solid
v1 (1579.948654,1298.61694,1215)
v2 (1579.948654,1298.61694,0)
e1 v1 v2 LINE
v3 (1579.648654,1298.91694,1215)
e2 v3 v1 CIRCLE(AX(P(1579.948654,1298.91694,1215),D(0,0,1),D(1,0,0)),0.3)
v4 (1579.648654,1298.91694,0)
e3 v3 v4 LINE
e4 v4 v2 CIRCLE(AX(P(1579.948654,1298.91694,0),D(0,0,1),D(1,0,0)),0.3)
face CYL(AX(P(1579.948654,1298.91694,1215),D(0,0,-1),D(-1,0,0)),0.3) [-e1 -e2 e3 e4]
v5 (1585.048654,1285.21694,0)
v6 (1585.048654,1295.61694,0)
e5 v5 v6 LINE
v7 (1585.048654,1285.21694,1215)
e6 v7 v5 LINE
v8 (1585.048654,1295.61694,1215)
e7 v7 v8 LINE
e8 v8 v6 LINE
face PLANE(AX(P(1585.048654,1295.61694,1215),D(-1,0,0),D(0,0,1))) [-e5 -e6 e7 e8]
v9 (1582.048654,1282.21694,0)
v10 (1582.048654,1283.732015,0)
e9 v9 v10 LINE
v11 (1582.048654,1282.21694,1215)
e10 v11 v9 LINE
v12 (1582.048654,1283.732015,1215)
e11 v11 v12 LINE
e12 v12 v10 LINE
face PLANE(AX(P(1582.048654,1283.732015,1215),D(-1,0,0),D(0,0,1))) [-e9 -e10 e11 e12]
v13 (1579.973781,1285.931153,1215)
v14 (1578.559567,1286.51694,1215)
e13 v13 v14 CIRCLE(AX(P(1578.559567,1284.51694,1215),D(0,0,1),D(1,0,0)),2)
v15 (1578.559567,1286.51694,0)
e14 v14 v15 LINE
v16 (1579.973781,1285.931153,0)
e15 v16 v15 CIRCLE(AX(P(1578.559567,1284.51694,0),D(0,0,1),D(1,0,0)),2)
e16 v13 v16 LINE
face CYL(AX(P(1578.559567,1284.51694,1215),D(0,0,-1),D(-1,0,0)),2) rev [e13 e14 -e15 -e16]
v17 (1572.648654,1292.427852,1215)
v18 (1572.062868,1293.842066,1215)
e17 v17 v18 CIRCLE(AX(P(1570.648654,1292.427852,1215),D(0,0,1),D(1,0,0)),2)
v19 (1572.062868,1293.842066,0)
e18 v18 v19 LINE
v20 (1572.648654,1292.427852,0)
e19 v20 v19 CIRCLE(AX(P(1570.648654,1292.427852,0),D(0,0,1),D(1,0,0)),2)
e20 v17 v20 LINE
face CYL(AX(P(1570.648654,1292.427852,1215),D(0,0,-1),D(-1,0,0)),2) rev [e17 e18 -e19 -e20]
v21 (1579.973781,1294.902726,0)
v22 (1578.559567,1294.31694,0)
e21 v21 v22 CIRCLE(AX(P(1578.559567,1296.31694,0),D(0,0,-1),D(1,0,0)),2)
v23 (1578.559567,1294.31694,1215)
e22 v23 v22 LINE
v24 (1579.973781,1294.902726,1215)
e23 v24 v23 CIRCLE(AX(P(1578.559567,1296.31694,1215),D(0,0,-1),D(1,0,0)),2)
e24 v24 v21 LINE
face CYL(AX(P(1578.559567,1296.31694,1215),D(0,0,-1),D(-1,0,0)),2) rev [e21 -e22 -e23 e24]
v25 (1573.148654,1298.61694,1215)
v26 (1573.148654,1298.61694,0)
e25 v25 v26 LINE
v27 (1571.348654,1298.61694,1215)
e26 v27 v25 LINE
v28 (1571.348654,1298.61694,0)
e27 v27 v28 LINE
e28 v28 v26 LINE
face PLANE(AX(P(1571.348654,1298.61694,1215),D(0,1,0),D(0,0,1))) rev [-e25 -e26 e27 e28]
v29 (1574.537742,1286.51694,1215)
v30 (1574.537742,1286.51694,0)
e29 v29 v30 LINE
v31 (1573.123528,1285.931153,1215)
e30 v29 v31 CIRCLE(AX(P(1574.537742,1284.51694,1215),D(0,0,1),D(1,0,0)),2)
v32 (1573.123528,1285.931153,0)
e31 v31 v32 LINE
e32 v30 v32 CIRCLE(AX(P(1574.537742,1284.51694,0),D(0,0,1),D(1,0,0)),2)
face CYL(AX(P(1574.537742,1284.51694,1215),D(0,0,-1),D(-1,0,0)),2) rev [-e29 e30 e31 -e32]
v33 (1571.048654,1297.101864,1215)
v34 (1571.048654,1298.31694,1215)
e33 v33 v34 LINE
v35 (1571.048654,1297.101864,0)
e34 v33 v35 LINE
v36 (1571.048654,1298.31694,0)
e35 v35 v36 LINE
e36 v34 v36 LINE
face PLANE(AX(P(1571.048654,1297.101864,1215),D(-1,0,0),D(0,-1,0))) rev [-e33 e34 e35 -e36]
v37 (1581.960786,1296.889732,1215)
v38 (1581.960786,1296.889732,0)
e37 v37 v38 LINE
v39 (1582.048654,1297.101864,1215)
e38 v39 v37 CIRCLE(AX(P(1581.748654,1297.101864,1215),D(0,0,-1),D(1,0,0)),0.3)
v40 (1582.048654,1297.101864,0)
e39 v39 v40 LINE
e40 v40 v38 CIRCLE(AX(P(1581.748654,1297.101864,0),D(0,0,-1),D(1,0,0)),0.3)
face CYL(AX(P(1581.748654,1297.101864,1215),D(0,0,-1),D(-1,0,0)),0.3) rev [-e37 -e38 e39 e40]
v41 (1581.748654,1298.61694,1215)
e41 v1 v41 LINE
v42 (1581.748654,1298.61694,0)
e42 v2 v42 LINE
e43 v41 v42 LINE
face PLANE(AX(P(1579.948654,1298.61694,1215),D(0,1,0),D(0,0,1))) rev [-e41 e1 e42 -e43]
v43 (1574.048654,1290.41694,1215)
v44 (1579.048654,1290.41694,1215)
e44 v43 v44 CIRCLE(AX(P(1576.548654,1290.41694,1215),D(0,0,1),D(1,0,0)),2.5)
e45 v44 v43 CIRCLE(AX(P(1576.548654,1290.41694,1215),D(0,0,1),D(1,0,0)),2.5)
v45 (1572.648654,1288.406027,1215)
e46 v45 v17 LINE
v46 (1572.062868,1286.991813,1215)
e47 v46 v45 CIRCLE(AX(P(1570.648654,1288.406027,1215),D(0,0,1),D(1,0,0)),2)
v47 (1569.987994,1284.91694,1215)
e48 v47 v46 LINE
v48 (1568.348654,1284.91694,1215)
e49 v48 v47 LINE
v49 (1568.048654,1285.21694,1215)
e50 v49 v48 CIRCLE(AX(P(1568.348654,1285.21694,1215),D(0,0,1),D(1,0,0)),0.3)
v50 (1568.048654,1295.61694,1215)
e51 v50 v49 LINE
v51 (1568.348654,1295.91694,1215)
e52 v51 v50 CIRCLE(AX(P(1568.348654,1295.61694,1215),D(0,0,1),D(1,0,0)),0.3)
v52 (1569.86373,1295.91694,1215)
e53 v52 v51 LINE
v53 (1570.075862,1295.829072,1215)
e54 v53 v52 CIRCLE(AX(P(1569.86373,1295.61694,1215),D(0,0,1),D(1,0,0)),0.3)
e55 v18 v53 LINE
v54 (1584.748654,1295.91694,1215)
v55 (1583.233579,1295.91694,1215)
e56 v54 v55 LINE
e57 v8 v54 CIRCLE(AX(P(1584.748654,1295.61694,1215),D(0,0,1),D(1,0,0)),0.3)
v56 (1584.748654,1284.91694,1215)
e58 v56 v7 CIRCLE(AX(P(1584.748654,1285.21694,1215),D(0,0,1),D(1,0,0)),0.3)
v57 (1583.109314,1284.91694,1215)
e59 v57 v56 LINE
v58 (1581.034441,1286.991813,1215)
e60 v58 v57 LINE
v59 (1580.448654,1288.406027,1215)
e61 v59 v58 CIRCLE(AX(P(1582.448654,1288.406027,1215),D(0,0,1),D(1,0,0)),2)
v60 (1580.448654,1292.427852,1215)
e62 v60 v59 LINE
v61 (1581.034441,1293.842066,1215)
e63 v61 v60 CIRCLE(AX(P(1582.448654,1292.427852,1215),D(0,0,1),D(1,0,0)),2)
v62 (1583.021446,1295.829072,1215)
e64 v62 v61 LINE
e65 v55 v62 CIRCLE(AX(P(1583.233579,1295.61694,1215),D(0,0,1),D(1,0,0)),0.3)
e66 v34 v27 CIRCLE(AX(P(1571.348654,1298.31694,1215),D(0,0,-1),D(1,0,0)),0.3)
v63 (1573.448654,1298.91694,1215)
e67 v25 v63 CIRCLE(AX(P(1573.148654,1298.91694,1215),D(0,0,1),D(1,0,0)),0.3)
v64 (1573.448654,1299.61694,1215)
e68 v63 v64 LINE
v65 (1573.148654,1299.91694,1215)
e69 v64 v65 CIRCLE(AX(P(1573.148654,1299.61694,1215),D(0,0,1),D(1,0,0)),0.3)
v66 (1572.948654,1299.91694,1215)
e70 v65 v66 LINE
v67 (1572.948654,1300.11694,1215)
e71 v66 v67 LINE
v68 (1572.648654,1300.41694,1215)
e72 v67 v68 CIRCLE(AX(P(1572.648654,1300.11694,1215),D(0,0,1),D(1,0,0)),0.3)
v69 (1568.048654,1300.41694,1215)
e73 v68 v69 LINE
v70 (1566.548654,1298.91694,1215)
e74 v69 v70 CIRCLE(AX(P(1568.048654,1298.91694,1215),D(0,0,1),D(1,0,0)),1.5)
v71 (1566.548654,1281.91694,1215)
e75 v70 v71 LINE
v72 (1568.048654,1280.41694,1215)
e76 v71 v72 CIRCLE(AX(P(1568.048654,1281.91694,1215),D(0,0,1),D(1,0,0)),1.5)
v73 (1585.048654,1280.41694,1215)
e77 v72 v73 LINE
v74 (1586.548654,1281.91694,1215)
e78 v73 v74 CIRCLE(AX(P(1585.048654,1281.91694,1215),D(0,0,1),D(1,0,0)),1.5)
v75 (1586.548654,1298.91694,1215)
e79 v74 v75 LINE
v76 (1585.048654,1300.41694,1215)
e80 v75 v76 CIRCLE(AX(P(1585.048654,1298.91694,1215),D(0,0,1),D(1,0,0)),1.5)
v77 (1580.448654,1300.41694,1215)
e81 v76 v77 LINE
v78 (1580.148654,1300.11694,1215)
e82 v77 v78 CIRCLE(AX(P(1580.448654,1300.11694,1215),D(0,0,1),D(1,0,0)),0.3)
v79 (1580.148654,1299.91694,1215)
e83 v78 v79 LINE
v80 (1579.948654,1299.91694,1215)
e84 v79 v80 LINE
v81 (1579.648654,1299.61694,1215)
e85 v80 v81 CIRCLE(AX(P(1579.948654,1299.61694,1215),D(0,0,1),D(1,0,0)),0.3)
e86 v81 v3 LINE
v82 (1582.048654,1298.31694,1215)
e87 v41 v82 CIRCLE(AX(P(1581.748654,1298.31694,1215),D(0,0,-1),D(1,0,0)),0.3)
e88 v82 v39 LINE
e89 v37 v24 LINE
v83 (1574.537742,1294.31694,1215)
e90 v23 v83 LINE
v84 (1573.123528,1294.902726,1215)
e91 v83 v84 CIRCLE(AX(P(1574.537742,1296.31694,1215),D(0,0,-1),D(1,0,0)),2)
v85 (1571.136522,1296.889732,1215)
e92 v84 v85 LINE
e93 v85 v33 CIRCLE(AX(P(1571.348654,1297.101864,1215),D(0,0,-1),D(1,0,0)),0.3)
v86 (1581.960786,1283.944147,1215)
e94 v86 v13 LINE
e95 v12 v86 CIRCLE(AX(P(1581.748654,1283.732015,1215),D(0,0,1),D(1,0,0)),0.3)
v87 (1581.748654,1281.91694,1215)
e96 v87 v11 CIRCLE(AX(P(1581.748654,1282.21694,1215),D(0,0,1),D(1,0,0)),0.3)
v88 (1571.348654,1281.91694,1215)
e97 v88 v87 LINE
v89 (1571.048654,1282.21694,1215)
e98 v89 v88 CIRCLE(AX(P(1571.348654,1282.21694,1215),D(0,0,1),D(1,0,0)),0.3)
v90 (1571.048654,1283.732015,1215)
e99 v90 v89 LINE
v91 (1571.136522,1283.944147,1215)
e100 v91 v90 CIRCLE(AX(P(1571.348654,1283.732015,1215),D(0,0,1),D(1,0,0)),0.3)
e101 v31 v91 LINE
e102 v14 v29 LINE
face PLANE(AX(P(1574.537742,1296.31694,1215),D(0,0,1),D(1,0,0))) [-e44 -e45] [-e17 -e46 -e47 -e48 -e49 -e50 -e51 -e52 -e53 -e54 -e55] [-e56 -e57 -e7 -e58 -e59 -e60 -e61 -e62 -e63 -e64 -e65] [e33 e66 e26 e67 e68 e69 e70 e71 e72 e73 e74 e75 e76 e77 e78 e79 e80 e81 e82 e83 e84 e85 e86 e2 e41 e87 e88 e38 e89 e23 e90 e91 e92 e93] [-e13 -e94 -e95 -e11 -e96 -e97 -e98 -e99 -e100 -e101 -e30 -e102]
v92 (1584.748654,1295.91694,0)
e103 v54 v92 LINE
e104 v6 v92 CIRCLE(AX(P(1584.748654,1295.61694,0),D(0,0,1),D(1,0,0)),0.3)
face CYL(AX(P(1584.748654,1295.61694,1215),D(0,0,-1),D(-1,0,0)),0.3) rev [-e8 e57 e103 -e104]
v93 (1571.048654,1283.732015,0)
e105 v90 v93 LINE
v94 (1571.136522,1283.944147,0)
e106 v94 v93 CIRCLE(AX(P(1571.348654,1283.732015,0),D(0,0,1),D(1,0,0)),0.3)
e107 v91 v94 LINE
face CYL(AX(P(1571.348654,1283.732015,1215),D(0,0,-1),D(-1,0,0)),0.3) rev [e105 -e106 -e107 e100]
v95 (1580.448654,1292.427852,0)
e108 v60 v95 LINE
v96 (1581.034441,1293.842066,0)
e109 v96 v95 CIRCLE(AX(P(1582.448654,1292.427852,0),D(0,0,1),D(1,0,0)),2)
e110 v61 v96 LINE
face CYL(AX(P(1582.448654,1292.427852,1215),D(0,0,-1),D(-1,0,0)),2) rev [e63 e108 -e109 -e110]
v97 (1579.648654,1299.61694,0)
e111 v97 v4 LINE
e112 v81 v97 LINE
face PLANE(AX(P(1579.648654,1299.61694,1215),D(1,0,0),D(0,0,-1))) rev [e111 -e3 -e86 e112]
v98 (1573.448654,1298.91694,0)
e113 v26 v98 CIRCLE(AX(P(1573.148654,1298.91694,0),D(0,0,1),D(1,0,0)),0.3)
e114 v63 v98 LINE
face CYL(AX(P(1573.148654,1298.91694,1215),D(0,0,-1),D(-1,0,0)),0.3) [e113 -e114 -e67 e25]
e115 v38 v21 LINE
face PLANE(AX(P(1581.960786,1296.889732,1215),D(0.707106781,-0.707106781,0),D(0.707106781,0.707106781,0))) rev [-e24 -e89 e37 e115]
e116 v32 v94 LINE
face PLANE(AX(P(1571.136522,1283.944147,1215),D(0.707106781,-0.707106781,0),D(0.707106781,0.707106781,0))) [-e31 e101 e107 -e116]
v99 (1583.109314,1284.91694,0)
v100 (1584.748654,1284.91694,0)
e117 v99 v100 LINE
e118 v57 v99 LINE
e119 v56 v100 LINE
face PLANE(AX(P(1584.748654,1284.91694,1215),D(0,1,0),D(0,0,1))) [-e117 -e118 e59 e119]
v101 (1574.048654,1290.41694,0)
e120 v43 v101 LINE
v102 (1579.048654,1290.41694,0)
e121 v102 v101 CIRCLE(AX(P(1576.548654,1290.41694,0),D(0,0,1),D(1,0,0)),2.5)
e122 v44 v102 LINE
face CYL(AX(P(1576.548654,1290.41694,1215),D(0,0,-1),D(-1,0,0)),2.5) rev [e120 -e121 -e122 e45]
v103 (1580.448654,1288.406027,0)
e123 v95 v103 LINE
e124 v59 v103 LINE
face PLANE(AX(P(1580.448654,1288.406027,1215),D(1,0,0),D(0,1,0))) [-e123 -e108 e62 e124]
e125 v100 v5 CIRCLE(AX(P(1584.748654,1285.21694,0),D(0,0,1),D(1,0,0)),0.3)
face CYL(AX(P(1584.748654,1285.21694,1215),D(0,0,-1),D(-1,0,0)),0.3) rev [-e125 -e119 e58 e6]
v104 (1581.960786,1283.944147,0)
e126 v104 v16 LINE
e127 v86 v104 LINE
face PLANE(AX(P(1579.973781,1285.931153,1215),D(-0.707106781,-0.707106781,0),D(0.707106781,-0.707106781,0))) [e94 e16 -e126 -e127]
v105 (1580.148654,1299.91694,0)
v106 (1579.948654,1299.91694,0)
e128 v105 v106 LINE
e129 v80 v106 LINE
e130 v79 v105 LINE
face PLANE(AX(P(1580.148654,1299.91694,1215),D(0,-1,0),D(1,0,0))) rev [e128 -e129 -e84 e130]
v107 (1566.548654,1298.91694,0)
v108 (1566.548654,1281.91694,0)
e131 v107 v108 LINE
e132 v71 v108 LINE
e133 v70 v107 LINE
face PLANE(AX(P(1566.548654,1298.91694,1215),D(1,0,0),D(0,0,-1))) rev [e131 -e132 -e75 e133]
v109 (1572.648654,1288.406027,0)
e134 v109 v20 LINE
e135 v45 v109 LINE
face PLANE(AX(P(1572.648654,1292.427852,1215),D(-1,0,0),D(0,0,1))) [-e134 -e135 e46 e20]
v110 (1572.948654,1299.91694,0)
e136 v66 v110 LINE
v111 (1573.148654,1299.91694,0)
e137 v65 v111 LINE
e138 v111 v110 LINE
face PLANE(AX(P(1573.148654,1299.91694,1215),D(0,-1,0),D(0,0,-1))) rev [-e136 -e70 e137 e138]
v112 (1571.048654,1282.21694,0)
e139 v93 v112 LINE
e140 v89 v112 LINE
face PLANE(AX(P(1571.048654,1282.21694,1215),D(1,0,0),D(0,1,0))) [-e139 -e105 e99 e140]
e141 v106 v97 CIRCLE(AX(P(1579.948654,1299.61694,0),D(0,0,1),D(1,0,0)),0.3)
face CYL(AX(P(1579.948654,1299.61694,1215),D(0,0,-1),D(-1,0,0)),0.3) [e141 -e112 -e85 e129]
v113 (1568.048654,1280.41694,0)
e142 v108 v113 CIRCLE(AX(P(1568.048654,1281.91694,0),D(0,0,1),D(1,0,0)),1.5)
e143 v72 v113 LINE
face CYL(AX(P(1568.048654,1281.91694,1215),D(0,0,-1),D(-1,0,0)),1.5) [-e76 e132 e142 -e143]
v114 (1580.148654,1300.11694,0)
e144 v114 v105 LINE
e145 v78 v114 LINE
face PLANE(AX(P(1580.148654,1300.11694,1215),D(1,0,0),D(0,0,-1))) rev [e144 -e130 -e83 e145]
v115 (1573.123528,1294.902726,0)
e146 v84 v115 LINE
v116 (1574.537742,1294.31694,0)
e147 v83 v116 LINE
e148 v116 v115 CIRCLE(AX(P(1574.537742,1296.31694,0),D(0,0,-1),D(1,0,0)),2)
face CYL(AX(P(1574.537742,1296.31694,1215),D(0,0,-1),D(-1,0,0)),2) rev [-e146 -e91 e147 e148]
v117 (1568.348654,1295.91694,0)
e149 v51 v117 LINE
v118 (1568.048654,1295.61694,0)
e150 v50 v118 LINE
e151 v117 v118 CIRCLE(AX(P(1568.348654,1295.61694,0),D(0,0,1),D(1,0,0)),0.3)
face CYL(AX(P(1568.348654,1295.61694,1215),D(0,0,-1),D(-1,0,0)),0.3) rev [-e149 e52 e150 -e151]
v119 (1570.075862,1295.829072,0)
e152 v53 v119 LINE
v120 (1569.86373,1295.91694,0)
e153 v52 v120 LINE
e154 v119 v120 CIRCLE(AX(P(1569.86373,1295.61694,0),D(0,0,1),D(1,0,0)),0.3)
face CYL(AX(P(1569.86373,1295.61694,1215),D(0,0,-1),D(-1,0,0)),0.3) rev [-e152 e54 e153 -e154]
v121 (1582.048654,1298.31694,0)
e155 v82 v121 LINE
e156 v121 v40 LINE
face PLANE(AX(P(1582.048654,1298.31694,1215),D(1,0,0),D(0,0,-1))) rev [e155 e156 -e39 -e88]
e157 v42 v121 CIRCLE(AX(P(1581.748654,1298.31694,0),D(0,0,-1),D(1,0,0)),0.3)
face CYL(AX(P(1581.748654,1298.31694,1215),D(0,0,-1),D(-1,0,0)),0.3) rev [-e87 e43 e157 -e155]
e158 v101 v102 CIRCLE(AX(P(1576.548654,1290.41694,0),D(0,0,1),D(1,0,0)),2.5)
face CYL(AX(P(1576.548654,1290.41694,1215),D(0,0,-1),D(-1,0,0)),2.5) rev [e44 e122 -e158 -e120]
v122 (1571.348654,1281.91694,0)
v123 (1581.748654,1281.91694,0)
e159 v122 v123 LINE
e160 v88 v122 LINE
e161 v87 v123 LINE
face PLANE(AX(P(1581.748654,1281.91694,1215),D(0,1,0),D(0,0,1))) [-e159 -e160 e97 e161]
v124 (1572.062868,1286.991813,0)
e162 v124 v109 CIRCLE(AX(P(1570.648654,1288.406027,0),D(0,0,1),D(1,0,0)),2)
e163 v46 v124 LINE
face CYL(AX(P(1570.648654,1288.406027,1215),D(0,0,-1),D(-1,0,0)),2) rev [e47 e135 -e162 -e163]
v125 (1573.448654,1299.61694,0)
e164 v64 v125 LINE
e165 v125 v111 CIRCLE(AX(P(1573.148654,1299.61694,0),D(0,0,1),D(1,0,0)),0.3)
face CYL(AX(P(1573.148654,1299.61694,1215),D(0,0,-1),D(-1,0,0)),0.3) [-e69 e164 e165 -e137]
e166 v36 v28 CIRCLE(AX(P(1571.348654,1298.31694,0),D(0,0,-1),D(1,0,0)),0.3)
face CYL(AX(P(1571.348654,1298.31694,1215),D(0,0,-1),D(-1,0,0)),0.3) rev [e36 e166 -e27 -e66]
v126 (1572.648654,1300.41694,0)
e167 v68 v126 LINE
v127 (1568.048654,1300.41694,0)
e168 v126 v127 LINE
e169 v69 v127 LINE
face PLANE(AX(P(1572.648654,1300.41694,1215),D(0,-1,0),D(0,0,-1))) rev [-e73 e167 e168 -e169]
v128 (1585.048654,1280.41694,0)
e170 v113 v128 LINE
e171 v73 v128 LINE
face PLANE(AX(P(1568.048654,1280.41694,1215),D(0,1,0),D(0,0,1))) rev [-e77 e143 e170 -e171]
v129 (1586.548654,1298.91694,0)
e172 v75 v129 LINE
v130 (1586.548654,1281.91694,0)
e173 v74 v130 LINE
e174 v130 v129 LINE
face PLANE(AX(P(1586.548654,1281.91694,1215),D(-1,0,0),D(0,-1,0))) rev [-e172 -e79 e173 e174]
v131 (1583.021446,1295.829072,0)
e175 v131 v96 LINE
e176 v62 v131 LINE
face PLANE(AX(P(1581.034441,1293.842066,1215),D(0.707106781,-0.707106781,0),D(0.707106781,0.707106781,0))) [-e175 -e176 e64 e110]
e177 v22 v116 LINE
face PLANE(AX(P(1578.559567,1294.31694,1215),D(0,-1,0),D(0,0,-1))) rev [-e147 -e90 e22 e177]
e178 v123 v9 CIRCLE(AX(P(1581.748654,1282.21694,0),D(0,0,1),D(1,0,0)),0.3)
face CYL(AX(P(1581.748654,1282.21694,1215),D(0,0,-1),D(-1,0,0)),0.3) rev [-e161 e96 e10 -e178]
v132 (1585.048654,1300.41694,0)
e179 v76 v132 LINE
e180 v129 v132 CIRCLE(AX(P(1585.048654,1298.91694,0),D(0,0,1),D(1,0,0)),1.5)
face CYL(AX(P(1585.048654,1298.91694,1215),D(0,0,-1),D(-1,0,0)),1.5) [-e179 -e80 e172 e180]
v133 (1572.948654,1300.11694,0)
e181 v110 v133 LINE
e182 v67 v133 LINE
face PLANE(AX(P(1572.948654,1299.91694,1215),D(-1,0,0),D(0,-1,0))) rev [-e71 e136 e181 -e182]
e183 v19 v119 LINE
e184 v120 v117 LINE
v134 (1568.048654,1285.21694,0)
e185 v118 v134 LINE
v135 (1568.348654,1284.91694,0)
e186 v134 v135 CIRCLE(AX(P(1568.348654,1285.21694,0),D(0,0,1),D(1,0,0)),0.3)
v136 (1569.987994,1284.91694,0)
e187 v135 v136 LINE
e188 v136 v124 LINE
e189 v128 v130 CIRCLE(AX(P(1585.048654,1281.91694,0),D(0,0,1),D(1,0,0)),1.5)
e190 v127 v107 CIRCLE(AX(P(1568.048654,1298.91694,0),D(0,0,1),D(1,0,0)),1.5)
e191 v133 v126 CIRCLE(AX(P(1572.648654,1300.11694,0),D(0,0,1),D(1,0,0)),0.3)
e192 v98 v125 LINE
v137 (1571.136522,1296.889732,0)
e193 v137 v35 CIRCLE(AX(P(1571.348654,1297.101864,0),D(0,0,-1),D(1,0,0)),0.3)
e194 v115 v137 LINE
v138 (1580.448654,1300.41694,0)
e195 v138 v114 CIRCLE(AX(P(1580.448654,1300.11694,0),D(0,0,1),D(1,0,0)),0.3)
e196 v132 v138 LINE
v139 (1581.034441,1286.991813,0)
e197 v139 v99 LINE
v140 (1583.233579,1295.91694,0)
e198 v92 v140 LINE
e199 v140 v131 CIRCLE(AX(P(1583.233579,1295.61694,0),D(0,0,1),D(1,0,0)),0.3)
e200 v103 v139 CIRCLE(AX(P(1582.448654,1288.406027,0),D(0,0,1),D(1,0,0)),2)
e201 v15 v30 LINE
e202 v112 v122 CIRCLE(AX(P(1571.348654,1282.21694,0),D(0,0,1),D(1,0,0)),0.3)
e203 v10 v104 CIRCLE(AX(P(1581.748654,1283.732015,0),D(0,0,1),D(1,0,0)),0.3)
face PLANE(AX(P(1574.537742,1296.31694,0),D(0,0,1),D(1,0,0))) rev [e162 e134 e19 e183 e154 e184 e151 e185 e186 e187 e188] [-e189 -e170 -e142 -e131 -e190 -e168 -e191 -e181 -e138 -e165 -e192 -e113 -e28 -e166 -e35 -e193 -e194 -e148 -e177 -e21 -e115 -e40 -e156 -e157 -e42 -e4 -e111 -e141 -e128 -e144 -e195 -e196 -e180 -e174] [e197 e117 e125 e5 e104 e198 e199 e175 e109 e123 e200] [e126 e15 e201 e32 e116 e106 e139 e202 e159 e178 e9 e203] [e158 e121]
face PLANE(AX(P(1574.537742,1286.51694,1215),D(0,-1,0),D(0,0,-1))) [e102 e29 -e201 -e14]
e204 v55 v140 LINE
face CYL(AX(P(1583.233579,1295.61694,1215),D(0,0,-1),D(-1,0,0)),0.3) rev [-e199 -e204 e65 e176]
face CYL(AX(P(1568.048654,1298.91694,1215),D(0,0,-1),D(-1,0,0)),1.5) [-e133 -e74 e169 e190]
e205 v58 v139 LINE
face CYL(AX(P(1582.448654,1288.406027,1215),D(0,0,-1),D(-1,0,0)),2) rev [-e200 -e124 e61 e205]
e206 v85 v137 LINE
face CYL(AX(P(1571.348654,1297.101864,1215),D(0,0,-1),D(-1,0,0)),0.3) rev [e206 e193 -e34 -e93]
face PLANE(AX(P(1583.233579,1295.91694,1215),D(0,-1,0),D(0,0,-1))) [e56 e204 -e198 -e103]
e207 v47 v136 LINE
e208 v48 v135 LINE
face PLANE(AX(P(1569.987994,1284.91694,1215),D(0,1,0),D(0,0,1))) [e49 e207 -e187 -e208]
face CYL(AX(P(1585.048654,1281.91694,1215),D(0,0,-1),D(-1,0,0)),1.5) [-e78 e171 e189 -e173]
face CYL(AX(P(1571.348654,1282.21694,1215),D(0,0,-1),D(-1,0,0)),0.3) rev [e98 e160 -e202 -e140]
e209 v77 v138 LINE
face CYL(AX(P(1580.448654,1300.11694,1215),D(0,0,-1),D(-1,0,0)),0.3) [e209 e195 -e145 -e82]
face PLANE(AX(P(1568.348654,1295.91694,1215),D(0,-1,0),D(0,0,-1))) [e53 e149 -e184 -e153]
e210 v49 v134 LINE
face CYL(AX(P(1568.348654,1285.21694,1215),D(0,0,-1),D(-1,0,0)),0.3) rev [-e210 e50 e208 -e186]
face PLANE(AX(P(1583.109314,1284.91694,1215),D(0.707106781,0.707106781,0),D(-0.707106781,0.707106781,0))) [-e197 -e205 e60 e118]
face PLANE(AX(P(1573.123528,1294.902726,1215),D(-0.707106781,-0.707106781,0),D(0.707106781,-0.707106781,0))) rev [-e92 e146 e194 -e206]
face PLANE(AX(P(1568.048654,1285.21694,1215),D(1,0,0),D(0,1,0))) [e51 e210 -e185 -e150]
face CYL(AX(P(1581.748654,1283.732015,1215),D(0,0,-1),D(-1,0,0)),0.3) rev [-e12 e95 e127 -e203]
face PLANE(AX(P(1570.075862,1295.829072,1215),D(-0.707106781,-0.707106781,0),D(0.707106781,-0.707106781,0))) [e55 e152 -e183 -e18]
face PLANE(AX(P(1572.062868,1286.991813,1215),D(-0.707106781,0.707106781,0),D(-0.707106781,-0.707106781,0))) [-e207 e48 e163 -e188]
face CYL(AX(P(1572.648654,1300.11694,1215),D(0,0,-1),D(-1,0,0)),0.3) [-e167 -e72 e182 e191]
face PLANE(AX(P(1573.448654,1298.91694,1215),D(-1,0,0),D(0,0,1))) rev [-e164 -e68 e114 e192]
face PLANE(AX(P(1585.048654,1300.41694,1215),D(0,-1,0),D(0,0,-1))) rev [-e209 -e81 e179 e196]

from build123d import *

# Parameters (mm, degrees)
SKETCH_1_R      = 2.5
EXTRUDE_1_DEPTH = 1215


with BuildPart() as part:
    # 草图1 → 凸台-拉伸1 (new body)
    with BuildSketch(Plane.XY):
        with BuildLine():
            Line((1573.123527995, 1294.902726123), (1571.136522226, 1296.889731891))
            ThreePointArc((1571.136522226, 1296.889731891), (1571.071490401, 1296.987058896), (1571.048654261, 1297.101863926))
            Line((1571.048654261, 1297.101863926), (1571.048654261, 1298.316939685))
            ThreePointArc((1571.048654261, 1298.316939685), (1571.136522226, 1298.52907172), (1571.348654261, 1298.616939685))
            Line((1571.348654261, 1298.616939685), (1573.148654261, 1298.616939685))
            ThreePointArc((1573.148654261, 1298.616939685), (1573.360786295, 1298.704807651), (1573.448654261, 1298.916939685))
            Line((1573.448654261, 1298.916939685), (1573.448654261, 1299.616939685))
            ThreePointArc((1573.448654261, 1299.616939685), (1573.360786295, 1299.82907172), (1573.148654261, 1299.916939685))
            Line((1573.148654261, 1299.916939685), (1572.948654261, 1299.916939685))
            Line((1572.948654261, 1299.916939685), (1572.948654261, 1300.116939685))
            ThreePointArc((1572.948654261, 1300.116939685), (1572.860786295, 1300.32907172), (1572.648654261, 1300.416939685))
            Line((1572.648654261, 1300.416939685), (1568.048654261, 1300.416939685))
            ThreePointArc((1568.048654261, 1300.416939685), (1566.987994089, 1299.977599857), (1566.548654261, 1298.916939685))
            Line((1566.548654261, 1298.916939685), (1566.548654261, 1281.916939685))
            ThreePointArc((1566.548654261, 1281.916939685), (1566.987994089, 1280.856279514), (1568.048654261, 1280.416939685))
            Line((1568.048654261, 1280.416939685), (1585.048654261, 1280.416939685))
            ThreePointArc((1585.048654261, 1280.416939685), (1586.109314432, 1280.856279514), (1586.548654261, 1281.916939685))
            Line((1586.548654261, 1281.916939685), (1586.548654261, 1298.916939685))
            ThreePointArc((1586.548654261, 1298.916939685), (1586.109314432, 1299.977599857), (1585.048654261, 1300.416939685))
            Line((1585.048654261, 1300.416939685), (1580.448654261, 1300.416939685))
            ThreePointArc((1580.448654261, 1300.416939685), (1580.236522226, 1300.32907172), (1580.148654261, 1300.116939685))
            Line((1580.148654261, 1300.116939685), (1580.148654261, 1299.916939685))
            Line((1580.148654261, 1299.916939685), (1579.948654261, 1299.916939685))
            ThreePointArc((1579.948654261, 1299.916939685), (1579.736522226, 1299.82907172), (1579.648654261, 1299.616939685))
            Line((1579.648654261, 1299.616939685), (1579.648654261, 1298.916939685))
            ThreePointArc((1579.648654261, 1298.916939685), (1579.736522226, 1298.704807651), (1579.94865426, 1298.616939685))
            Line((1579.94865426, 1298.616939685), (1581.748654261, 1298.616939685))
            ThreePointArc((1581.748654261, 1298.616939685), (1581.960786295, 1298.52907172), (1582.048654261, 1298.316939685))
            Line((1582.048654261, 1298.316939685), (1582.048654261, 1297.101863926))
            ThreePointArc((1582.048654261, 1297.101863926), (1582.02581812, 1296.987058896), (1581.960786295, 1296.889731891))
            Line((1581.960786295, 1296.889731891), (1579.973780526, 1294.902726123))
            ThreePointArc((1579.973780526, 1294.902726123), (1579.324933829, 1294.46918062), (1578.559566964, 1294.316939685))
            Line((1578.559566964, 1294.316939685), (1574.537741557, 1294.316939685))
            ThreePointArc((1574.537741557, 1294.316939685), (1573.772374693, 1294.46918062), (1573.123527995, 1294.902726123))
        make_face()
        with Locations((1576.548654261, 1290.416939685)):
            Circle(SKETCH_1_R, mode=Mode.SUBTRACT)
        with BuildLine():
            Line((1572.648654261, 1292.427852389), (1572.648654261, 1288.406026982))
            ThreePointArc((1572.648654261, 1288.406026982), (1572.496413326, 1287.640660117), (1572.062867823, 1286.99181342))
            Line((1572.062867823, 1286.99181342), (1569.987994089, 1284.916939685))
            Line((1569.987994089, 1284.916939685), (1568.348654261, 1284.916939685))
            ThreePointArc((1568.348654261, 1284.916939685), (1568.136522226, 1285.004807651), (1568.048654261, 1285.216939685))
            Line((1568.048654261, 1285.216939685), (1568.048654261, 1295.616939685))
            ThreePointArc((1568.048654261, 1295.616939685), (1568.136522226, 1295.82907172), (1568.348654261, 1295.916939685))
            Line((1568.348654261, 1295.916939685), (1569.86373002, 1295.916939685))
            ThreePointArc((1569.86373002, 1295.916939685), (1569.97853505, 1295.894103545), (1570.075862055, 1295.82907172))
            Line((1570.075862055, 1295.82907172), (1572.062867823, 1293.842065951))
            ThreePointArc((1572.062867823, 1293.842065951), (1572.496413326, 1293.193219254), (1572.648654261, 1292.427852389))
        make_face(mode=Mode.SUBTRACT)
        with BuildLine():
            Line((1581.034440698, 1293.842065951), (1583.021446467, 1295.82907172))
            ThreePointArc((1583.021446467, 1295.82907172), (1583.118773471, 1295.894103545), (1583.233578501, 1295.916939685))
            Line((1583.233578501, 1295.916939685), (1584.748654261, 1295.916939685))
            ThreePointArc((1584.748654261, 1295.916939685), (1584.960786295, 1295.82907172), (1585.048654261, 1295.616939685))
            Line((1585.048654261, 1295.616939685), (1585.048654261, 1285.216939685))
            ThreePointArc((1585.048654261, 1285.216939685), (1584.960786295, 1285.004807651), (1584.748654261, 1284.916939685))
            Line((1584.748654261, 1284.916939685), (1583.109314432, 1284.916939685))
            Line((1583.109314432, 1284.916939685), (1581.034440698, 1286.99181342))
            ThreePointArc((1581.034440698, 1286.99181342), (1580.600895196, 1287.640660117), (1580.448654261, 1288.406026982))
            Line((1580.448654261, 1288.406026982), (1580.448654261, 1292.427852389))
            ThreePointArc((1580.448654261, 1292.427852389), (1580.600895196, 1293.193219254), (1581.034440698, 1293.842065951))
        make_face(mode=Mode.SUBTRACT)
        with BuildLine():
            Line((1574.537741557, 1286.516939685), (1578.559566964, 1286.516939685))
            ThreePointArc((1578.559566964, 1286.516939685), (1579.324933829, 1286.36469875), (1579.973780526, 1285.931153248))
            Line((1579.973780526, 1285.931153248), (1581.960786295, 1283.944147479))
            ThreePointArc((1581.960786295, 1283.944147479), (1582.02581812, 1283.846820475), (1582.048654261, 1283.732015445))
            Line((1582.048654261, 1283.732015445), (1582.048654261, 1282.216939685))
            ThreePointArc((1582.048654261, 1282.216939685), (1581.960786295, 1282.004807651), (1581.748654261, 1281.916939685))
            Line((1581.748654261, 1281.916939685), (1571.348654261, 1281.916939685))
            ThreePointArc((1571.348654261, 1281.916939685), (1571.136522226, 1282.004807651), (1571.048654261, 1282.216939685))
            Line((1571.048654261, 1282.216939685), (1571.048654261, 1283.732015445))
            ThreePointArc((1571.048654261, 1283.732015445), (1571.071490401, 1283.846820475), (1571.136522226, 1283.944147479))
            Line((1571.136522226, 1283.944147479), (1573.123527995, 1285.931153248))
            ThreePointArc((1573.123527995, 1285.931153248), (1573.772374693, 1286.36469875), (1574.537741557, 1286.516939685))
        make_face(mode=Mode.SUBTRACT)
    extrude(amount=EXTRUDE_1_DEPTH)


solid = part.part
